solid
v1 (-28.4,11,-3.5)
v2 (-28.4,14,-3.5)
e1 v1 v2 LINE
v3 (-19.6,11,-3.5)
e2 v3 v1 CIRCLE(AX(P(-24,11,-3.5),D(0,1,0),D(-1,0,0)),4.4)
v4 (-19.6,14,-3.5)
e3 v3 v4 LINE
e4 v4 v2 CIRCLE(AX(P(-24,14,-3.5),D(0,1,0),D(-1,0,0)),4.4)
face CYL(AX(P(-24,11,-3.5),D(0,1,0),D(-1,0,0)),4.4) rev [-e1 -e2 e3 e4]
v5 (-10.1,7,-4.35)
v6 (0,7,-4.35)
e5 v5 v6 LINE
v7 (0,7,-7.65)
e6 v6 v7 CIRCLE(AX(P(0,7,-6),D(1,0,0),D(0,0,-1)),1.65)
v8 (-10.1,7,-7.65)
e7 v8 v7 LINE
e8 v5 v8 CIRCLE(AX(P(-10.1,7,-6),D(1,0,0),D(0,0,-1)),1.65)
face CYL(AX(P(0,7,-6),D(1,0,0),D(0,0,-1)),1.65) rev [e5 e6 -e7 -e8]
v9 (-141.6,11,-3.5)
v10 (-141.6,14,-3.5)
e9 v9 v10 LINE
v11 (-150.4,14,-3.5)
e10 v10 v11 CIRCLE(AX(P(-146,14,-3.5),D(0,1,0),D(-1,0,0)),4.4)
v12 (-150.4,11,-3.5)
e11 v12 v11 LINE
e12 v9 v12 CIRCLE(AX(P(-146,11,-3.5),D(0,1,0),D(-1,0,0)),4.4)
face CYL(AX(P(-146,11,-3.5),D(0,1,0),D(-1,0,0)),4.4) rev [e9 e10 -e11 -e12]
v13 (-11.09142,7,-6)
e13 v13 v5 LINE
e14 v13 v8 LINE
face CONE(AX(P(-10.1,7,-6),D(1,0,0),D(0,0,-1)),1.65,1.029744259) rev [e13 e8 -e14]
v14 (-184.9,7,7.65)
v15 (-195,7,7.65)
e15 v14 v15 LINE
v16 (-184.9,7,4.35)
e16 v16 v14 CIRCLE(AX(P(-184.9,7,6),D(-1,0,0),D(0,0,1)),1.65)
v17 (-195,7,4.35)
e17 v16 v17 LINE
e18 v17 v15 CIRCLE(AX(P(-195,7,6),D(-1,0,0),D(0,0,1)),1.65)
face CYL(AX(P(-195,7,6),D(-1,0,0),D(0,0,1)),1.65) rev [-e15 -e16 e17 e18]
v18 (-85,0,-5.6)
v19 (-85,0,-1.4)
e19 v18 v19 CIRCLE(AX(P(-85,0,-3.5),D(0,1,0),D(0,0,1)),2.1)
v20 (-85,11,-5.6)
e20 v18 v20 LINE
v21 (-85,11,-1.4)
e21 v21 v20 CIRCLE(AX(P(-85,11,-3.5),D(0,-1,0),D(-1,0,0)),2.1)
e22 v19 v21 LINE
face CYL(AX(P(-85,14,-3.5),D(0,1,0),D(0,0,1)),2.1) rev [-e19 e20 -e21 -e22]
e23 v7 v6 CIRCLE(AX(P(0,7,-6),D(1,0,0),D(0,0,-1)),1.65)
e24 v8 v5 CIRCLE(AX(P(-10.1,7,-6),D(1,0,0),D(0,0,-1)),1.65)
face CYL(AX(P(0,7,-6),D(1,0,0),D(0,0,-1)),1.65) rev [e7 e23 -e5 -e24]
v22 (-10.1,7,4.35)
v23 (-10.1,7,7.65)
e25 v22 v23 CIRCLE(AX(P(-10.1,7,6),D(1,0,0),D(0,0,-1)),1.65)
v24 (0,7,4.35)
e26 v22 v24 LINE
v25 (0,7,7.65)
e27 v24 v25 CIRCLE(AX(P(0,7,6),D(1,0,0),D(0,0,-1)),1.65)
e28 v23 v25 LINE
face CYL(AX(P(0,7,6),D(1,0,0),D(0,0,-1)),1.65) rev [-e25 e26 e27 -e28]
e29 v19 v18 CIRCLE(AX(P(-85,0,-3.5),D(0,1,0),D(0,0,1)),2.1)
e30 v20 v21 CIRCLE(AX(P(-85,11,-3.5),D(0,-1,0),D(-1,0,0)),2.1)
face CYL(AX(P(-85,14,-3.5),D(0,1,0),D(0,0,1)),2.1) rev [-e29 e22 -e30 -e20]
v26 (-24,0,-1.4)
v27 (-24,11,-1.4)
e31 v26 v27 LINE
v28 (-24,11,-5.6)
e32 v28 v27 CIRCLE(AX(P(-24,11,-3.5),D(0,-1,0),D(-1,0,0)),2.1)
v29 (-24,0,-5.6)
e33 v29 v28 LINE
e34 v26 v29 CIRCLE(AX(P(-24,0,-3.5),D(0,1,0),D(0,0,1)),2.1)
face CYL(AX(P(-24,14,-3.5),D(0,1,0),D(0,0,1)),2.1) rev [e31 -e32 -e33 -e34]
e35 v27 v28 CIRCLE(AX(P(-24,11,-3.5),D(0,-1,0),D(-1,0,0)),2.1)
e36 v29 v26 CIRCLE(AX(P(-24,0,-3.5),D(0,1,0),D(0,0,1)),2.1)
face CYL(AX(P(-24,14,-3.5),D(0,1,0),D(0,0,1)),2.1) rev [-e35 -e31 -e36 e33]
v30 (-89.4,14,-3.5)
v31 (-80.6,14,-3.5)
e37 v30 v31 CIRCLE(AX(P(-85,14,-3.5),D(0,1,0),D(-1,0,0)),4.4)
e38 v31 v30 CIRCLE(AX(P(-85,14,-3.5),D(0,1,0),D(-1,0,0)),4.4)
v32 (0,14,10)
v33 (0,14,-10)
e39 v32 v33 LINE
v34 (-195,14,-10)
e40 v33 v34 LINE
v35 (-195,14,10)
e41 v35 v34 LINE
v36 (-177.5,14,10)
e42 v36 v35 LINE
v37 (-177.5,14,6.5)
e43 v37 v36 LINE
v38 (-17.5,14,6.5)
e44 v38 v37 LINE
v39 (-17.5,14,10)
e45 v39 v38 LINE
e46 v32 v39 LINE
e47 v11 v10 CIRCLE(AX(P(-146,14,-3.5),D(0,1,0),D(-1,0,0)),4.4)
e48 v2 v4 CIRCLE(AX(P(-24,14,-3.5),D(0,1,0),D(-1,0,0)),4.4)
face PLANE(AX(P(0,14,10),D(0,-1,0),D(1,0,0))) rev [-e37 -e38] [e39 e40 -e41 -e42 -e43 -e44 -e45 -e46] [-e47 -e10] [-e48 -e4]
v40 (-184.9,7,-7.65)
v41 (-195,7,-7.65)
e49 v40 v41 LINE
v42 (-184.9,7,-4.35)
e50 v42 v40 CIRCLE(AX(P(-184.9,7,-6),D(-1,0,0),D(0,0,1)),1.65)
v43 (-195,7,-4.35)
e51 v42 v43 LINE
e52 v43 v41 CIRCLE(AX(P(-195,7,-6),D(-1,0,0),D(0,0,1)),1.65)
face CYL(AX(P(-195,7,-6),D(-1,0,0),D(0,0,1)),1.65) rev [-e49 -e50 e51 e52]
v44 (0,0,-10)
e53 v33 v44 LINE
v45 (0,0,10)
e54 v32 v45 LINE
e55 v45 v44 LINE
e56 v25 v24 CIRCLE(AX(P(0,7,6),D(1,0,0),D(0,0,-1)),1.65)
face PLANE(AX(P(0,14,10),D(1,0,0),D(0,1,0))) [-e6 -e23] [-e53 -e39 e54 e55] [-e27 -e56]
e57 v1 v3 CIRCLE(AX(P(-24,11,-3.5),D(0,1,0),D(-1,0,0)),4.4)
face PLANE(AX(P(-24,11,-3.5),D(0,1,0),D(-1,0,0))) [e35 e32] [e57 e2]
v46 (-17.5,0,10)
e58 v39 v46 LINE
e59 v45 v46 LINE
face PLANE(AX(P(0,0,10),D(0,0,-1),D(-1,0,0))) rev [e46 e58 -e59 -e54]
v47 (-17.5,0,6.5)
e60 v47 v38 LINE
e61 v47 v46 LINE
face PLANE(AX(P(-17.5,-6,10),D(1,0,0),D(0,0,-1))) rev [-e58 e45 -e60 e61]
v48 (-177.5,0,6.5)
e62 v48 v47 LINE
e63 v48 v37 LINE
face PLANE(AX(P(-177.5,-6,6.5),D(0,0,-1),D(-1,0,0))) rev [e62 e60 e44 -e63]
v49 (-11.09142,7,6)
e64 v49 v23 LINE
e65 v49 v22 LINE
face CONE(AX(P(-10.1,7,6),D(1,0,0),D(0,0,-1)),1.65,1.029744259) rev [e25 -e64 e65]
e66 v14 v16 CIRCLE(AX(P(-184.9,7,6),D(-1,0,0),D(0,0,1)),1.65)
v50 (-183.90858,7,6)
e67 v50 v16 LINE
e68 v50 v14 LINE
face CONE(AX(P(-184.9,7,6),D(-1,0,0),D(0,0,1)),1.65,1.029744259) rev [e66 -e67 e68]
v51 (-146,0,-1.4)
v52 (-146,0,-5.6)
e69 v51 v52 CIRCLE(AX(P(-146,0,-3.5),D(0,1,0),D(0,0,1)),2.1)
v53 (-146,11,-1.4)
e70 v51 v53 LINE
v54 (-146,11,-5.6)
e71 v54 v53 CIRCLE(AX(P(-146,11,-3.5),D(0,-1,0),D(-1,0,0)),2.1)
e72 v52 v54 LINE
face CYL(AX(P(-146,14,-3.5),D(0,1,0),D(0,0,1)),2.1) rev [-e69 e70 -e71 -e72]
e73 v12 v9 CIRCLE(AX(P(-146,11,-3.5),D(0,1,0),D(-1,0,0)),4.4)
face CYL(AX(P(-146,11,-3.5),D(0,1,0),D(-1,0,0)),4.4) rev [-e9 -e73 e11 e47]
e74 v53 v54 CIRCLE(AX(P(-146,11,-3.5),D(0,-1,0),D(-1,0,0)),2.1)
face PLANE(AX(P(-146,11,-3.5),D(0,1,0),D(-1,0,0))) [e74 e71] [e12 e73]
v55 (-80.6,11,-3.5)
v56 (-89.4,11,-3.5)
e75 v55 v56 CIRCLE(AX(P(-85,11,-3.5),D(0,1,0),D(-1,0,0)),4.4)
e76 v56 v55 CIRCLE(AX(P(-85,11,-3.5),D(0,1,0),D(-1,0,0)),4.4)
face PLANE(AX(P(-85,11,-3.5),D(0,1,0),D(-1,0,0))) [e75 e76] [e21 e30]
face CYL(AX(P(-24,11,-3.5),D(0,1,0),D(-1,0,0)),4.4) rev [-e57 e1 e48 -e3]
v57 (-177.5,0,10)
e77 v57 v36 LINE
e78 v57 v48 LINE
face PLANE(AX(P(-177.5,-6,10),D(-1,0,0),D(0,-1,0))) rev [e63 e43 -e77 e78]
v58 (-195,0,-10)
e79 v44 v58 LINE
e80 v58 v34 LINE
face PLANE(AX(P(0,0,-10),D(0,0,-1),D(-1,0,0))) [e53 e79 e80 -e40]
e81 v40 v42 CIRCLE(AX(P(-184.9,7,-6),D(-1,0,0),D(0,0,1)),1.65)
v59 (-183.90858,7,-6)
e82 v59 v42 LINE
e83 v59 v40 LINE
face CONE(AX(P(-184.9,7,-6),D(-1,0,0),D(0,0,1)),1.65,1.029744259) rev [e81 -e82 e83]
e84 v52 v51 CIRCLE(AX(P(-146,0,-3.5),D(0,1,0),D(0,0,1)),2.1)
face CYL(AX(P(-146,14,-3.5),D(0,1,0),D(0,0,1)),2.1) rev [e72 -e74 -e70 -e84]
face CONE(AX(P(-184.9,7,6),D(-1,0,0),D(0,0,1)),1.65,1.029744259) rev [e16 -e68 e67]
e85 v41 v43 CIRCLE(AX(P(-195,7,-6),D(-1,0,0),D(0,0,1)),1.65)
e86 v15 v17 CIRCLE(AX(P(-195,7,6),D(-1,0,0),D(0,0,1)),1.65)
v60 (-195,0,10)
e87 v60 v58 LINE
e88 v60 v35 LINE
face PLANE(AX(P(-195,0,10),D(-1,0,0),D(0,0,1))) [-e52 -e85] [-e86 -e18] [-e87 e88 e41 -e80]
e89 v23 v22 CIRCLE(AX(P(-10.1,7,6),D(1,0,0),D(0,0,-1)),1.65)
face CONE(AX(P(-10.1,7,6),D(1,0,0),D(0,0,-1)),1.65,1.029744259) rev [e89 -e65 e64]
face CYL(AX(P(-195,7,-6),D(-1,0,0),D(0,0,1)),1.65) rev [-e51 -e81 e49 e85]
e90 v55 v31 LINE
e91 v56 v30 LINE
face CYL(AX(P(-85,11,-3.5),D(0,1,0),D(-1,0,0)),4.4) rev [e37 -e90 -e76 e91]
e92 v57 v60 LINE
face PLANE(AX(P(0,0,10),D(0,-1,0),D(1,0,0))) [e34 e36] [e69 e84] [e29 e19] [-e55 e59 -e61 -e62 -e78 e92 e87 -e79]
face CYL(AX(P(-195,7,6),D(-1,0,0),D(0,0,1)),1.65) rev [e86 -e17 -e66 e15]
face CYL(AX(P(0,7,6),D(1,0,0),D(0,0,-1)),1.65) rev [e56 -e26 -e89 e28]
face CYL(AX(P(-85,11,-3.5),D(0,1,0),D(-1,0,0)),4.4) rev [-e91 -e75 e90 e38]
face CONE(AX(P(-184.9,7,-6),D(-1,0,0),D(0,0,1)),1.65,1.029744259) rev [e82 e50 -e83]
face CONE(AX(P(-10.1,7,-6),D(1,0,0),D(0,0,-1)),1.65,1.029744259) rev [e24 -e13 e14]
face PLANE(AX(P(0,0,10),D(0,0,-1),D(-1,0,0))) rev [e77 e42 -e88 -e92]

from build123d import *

# Parameters (mm, degrees)
SKETCH1_W             = 195
SKETCH1_H             = 14
EXTRUDE_THIN1_DEPTH   = 10
M4_TAPPED_HOLE1_D     = 3.3
M4_TAPPED_HOLE1_DEPTH = 10.1
M4_TAPPED_HOLE1_TIP   = 0.991420021
M4_TAPPED_HOLE2_D     = 3.3
M4_TAPPED_HOLE2_DEPTH = 10.1
M4_TAPPED_HOLE2_TIP   = 0.991420021
M5_TAPPED_HOLE1_D     = 4.2
SKETCH9_R             = 4.4
CUT_EXTRUDE1_DEPTH    = 3
SKETCH10_W            = 160
SKETCH10_H            = 3.5
CUT_EXTRUDE2_DEPTH    = 20


with BuildPart() as part:
    # Sketch1 → Extrude-Thin1 (new, symmetric)
    with BuildSketch(Plane.XY):
        with Locations((-97.5, 7)):
            Rectangle(SKETCH1_W, SKETCH1_H)
    extrude(amount=EXTRUDE_THIN1_DEPTH, both=True)

    # M4 Tapped Hole1
    with Locations(Plane.ZY.offset(195)):
        with Locations((-6, 7), (6, 7)):
            Hole(M4_TAPPED_HOLE1_D / 2, depth=M4_TAPPED_HOLE1_DEPTH)
            with Locations((0, 0, -(M4_TAPPED_HOLE1_DEPTH + M4_TAPPED_HOLE1_TIP / 2))):  # 118° drill point
                Cone(0, M4_TAPPED_HOLE1_D / 2, M4_TAPPED_HOLE1_TIP, mode=Mode.SUBTRACT)

    # M4 Tapped Hole2
    with Locations(Plane(origin=(0, 0, 0), x_dir=(0, 0, -1), z_dir=(1, 0, 0))):
        with Locations((-6, 7), (6, 7)):
            Hole(M4_TAPPED_HOLE2_D / 2, depth=M4_TAPPED_HOLE2_DEPTH)
            with Locations((0, 0, -(M4_TAPPED_HOLE2_DEPTH + M4_TAPPED_HOLE2_TIP / 2))):  # 118° drill point
                Cone(0, M4_TAPPED_HOLE2_D / 2, M4_TAPPED_HOLE2_TIP, mode=Mode.SUBTRACT)

    # M5 Tapped Hole1 (through all)
    with Locations(Plane(origin=(0, 14, 0), x_dir=(1, 0, 0), z_dir=(0, 1, 0))):
        with Locations((-146, 3.5), (-85, 3.5), (-24, 3.5)):
            Hole(M5_TAPPED_HOLE1_D / 2)

    # Sketch9 → Cut-Extrude1 (cut)
    with BuildSketch(Plane(origin=(0, 14, 0), x_dir=(1, 0, 0), z_dir=(0, 1, 0))):
        with Locations(Location((-146, 3.5, 0), (0, 0, 180))):
            Circle(SKETCH9_R)
        with Locations(Location((-85, 3.5, 0), (0, 0, 180))):
            Circle(SKETCH9_R)
        with Locations(Location((-24, 3.5, 0), (0, 0, 180))):
            Circle(SKETCH9_R)
    extrude(amount=-CUT_EXTRUDE1_DEPTH, mode=Mode.SUBTRACT)

    # Sketch10 → Cut-Extrude2 (cut)
    with BuildSketch(Plane(origin=(0, 14, 0), x_dir=(1, 0, 0), z_dir=(0, 1, 0))):
        with Locations((-97.5, -8.25)):
            Rectangle(SKETCH10_W, SKETCH10_H)
    extrude(amount=-CUT_EXTRUDE2_DEPTH, mode=Mode.SUBTRACT)


solid = part.part
